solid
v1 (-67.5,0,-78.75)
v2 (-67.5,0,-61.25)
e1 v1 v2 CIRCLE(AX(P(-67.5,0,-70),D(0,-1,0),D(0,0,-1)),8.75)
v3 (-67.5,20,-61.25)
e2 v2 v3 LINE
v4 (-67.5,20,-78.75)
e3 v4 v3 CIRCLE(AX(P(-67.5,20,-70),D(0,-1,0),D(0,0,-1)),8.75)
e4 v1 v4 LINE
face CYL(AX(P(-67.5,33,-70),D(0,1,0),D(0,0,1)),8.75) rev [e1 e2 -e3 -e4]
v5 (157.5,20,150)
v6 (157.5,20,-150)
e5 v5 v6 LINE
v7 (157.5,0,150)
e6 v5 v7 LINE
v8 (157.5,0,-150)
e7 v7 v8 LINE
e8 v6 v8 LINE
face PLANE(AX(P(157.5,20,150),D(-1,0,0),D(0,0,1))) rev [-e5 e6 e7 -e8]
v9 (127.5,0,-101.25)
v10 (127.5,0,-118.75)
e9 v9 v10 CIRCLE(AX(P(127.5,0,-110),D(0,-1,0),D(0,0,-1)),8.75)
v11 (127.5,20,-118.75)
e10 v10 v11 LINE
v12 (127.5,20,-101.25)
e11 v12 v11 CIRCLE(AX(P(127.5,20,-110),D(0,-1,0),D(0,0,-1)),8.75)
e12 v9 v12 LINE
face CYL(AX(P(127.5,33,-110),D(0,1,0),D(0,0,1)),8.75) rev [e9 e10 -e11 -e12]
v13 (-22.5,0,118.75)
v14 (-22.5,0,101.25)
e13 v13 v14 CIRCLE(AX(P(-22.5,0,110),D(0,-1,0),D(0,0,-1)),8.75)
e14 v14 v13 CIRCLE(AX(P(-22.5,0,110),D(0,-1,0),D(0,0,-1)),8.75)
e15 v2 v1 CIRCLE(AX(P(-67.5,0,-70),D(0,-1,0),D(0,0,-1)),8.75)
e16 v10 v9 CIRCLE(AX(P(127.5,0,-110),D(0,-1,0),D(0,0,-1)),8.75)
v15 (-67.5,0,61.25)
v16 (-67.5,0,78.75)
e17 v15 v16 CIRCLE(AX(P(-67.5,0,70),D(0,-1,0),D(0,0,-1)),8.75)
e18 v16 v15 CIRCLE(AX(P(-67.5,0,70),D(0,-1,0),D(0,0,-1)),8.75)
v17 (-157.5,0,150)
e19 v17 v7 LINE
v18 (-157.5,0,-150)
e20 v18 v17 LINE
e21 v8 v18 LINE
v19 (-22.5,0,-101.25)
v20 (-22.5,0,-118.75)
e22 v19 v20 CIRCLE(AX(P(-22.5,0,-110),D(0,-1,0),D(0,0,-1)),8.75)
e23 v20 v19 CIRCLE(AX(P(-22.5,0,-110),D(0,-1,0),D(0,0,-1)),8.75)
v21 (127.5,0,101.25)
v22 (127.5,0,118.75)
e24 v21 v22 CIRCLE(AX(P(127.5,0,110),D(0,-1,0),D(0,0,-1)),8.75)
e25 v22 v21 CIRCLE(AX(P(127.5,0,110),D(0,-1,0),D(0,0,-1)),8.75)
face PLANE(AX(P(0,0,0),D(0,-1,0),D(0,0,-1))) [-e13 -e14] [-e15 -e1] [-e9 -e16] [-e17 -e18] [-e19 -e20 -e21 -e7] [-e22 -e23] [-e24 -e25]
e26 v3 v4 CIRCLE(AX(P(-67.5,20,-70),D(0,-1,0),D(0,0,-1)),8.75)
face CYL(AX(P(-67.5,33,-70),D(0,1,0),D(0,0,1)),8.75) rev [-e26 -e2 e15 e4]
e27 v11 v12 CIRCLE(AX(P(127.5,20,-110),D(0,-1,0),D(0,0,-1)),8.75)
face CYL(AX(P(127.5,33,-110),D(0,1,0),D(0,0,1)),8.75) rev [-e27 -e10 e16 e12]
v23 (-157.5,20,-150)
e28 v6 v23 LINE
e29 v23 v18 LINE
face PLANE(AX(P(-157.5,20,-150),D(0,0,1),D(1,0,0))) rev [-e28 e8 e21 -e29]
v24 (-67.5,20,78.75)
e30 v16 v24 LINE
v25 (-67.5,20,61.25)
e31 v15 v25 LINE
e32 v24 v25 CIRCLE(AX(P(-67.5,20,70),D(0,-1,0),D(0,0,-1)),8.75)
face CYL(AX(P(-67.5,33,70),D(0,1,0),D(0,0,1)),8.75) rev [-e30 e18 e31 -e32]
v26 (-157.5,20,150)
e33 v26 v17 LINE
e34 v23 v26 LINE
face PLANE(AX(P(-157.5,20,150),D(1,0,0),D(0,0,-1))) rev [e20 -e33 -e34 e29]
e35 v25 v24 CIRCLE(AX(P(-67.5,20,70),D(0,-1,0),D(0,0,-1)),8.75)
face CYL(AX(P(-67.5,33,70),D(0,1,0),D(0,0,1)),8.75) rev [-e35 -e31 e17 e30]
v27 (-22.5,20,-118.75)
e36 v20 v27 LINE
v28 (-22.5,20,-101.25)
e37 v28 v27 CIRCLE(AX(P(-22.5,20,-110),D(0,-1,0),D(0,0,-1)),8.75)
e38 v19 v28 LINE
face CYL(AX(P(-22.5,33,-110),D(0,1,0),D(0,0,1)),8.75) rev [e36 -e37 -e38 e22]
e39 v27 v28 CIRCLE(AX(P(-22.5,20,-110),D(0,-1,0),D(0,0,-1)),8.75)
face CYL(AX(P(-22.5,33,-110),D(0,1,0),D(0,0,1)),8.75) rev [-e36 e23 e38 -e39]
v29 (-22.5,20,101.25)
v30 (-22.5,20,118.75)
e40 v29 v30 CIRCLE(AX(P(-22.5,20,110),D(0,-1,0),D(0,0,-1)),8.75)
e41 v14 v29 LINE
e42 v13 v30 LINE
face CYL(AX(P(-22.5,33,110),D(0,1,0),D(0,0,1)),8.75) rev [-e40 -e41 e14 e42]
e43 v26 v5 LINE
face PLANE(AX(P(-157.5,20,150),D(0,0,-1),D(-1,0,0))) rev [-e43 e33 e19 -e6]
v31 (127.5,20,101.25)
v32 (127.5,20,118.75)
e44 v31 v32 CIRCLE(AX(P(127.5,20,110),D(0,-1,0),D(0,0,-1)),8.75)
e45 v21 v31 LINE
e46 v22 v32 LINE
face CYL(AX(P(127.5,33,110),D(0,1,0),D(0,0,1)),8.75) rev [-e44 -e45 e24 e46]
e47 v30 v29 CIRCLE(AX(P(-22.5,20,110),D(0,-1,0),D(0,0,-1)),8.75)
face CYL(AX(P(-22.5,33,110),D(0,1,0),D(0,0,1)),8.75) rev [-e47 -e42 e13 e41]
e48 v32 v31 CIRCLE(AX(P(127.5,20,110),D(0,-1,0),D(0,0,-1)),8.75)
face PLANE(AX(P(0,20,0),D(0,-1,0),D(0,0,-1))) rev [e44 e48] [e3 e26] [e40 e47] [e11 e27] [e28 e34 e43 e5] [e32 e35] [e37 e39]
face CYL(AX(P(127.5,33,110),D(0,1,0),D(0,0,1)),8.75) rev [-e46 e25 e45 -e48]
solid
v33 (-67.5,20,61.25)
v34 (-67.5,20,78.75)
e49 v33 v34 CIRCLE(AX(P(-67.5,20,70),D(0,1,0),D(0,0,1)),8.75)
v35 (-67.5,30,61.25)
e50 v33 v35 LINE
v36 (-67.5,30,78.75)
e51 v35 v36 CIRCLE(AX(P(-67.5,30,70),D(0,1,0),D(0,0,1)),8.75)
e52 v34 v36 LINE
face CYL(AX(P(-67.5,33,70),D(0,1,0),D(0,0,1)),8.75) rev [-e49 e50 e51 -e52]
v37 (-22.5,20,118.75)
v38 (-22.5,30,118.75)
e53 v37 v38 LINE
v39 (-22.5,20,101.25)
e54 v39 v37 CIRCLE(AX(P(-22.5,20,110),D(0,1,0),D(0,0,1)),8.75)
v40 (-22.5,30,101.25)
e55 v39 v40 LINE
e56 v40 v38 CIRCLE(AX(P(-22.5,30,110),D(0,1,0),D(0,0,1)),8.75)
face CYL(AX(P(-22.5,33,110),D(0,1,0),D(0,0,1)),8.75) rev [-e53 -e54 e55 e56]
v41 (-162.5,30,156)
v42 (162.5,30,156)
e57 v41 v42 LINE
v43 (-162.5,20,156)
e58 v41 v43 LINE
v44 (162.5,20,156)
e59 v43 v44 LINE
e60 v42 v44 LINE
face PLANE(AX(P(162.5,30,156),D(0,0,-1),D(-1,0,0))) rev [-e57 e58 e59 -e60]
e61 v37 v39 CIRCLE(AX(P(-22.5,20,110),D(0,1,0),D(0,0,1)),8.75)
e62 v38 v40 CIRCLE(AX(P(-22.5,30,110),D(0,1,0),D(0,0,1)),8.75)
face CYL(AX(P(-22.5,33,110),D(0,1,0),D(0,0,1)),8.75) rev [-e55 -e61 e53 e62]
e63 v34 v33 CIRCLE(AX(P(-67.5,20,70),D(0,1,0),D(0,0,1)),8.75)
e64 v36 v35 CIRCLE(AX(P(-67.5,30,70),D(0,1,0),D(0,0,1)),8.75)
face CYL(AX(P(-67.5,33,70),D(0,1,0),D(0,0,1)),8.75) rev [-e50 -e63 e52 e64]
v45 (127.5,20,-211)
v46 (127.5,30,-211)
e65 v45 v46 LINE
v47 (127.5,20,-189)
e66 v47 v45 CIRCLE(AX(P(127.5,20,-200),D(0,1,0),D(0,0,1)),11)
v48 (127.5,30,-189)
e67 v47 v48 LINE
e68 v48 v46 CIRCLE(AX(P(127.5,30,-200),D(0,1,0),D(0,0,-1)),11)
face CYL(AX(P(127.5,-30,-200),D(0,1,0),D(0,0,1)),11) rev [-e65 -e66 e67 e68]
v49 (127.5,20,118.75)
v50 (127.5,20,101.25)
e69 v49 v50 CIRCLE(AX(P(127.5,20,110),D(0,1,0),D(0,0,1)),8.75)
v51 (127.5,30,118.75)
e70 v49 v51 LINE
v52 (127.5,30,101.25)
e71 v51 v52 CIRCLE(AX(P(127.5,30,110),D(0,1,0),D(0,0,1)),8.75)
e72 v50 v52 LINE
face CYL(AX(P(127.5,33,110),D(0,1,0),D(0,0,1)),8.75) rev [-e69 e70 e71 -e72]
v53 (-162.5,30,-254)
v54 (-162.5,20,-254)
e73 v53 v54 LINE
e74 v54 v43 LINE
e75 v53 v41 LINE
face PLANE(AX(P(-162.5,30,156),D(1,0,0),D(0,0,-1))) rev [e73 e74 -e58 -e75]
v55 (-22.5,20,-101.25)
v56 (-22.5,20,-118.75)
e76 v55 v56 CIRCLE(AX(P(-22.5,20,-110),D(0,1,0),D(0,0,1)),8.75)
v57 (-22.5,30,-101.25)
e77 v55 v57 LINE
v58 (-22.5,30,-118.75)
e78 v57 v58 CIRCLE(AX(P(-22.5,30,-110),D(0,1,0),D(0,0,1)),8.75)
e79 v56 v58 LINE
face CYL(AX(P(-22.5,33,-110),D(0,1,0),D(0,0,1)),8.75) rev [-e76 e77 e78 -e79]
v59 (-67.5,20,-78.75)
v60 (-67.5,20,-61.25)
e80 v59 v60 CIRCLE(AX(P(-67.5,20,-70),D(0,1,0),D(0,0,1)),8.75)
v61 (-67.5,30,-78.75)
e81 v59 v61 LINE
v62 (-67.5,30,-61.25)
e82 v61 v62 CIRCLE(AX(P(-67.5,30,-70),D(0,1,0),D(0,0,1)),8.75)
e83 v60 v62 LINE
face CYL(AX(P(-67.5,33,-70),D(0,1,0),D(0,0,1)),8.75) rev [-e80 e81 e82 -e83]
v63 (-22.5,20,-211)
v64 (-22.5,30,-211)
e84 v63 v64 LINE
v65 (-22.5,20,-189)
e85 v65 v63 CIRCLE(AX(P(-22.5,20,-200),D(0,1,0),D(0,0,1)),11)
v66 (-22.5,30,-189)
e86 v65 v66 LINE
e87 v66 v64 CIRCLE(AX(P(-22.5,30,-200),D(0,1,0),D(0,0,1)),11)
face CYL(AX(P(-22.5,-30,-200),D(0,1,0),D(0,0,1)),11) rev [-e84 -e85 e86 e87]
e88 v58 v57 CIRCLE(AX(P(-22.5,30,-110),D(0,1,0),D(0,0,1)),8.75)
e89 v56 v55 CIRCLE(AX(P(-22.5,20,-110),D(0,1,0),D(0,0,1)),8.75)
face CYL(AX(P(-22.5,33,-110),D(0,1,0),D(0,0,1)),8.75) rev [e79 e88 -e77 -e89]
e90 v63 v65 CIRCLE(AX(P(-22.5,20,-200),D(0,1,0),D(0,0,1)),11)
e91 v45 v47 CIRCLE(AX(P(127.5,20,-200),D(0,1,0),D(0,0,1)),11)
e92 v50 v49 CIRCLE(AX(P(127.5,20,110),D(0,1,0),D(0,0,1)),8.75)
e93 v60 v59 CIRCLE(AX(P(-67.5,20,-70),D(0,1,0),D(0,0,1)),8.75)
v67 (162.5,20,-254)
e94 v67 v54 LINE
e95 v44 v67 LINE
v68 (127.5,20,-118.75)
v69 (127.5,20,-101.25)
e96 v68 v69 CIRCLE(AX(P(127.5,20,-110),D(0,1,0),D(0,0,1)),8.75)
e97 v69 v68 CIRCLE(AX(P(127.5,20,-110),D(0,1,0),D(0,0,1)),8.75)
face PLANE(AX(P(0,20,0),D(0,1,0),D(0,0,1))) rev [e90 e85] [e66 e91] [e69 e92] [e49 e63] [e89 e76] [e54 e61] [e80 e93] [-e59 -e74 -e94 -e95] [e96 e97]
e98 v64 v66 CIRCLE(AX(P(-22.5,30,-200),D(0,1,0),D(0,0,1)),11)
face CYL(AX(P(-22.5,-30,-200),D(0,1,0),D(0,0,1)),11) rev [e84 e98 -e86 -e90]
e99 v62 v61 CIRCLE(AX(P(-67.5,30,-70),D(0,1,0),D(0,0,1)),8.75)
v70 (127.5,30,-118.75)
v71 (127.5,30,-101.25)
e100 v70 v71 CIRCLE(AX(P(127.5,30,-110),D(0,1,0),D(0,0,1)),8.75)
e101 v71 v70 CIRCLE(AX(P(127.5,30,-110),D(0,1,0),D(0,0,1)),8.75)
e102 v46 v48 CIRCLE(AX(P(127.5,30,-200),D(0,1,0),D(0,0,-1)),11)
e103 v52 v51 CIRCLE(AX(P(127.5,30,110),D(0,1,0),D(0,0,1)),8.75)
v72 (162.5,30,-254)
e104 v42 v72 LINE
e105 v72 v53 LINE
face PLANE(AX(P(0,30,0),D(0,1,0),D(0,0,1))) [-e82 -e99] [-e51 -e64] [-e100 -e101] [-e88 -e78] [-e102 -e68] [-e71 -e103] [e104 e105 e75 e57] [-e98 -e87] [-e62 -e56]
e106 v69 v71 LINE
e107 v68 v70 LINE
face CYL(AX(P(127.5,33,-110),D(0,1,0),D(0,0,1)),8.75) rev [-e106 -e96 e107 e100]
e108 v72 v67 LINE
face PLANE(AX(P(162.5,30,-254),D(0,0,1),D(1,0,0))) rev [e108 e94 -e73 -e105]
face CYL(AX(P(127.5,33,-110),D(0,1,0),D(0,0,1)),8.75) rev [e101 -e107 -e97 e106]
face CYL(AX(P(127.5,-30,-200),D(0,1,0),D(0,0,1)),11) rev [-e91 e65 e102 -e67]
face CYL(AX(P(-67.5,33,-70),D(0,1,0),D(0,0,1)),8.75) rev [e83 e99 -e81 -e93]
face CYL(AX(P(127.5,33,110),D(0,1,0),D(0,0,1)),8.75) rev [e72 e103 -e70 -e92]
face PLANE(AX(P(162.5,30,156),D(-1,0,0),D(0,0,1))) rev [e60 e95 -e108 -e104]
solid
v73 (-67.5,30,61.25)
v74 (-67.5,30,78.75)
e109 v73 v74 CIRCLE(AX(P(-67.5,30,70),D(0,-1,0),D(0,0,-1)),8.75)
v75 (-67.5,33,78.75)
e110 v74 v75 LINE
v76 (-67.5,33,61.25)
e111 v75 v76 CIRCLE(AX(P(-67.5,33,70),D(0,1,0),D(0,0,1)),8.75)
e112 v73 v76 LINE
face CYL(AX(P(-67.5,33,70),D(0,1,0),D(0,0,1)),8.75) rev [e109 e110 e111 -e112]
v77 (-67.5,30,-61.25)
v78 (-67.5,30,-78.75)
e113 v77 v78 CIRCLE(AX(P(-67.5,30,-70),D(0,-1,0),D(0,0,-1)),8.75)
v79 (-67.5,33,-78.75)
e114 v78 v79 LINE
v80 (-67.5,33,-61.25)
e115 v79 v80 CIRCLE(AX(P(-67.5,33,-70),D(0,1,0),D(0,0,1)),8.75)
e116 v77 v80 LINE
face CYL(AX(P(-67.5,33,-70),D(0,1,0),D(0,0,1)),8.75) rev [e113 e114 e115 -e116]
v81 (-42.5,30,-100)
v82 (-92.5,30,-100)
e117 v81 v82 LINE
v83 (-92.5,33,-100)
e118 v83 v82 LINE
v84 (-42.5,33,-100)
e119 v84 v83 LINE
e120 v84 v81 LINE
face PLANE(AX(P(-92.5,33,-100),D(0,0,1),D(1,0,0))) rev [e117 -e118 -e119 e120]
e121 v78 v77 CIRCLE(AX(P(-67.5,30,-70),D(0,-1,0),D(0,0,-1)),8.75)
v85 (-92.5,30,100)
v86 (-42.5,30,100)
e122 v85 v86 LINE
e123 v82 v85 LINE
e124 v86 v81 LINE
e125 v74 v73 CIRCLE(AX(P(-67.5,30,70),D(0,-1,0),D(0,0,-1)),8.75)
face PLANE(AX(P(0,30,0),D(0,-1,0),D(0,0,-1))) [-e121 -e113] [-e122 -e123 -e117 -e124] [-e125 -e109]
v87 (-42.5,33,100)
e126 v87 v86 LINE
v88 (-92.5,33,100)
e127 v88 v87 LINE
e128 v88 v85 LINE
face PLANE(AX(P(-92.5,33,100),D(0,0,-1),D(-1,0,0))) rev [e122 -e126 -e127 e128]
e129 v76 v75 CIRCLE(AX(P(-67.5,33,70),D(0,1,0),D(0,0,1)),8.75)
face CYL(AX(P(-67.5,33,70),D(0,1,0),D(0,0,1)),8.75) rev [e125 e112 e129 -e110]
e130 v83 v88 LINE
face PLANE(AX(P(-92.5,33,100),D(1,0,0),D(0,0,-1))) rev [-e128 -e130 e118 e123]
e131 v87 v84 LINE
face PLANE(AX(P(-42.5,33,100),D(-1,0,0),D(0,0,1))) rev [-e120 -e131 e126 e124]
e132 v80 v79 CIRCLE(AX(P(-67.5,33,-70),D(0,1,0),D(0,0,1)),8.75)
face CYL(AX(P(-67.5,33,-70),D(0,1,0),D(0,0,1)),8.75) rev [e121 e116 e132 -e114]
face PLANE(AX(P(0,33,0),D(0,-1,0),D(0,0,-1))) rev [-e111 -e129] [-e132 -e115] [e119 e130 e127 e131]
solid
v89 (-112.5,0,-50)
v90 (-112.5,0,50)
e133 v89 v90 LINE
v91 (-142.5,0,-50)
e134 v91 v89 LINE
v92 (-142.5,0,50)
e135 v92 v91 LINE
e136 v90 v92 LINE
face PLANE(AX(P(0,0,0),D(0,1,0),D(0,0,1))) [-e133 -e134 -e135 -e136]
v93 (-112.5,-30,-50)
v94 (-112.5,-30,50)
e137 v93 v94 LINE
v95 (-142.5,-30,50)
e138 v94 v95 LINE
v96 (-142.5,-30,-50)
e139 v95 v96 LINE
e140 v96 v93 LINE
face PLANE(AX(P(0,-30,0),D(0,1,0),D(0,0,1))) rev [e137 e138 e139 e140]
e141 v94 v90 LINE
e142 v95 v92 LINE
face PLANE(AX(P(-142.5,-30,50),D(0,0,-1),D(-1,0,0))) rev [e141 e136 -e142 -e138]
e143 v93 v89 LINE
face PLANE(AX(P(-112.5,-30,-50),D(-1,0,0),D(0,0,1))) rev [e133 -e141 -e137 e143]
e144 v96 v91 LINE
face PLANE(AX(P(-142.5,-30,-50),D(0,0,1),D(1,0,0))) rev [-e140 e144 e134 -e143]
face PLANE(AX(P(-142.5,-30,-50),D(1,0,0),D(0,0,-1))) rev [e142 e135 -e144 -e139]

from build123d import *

# Parameters (mm, degrees)
SKETCH_1_W                   = 315
SKETCH_1_H                   = 300
EXTRUDE_1_DEPTH              = 20
SKETCH_2_W                   = 325
SKETCH_2_H                   = 410
EXTRUDE_2_DEPTH              = 10
SKETCH_3_W                   = 50
SKETCH_3_H                   = 200
EXTRUDE_3_DEPTH              = 3
SKETCH_4_W                   = 30
SKETCH_4_H                   = 100
EXTRUDE_4_DEPTH              = 30
HOLE_WIZARD_M20_1_AT_2_COUNT = 2
HOLE_WIZARD_M20_1_AT_2_PITCH = 60.207972894
HOLE_WIZARD_M20_1_AT_3_COUNT = 2
HOLE_WIZARD_M20_1_AT_3_PITCH = 185.539753153
HOLE_WIZARD_M20_1_AT_4_COUNT = 2
HOLE_WIZARD_M20_1_AT_4_PITCH = 140
HOLE_WIZARD_M20_1_AT_5_COUNT = 2
HOLE_WIZARD_M20_1_AT_5_PITCH = 265.377090194
HOLE_WIZARD_M20_1_AT_6_COUNT = 2
HOLE_WIZARD_M20_1_AT_6_PITCH = 199.060292374
SKETCH_5_R                   = 11
CUT_EXTRUDE_1_DEPTH          = 308.444710477


with BuildPart() as part:
    # 草图1 → 凸台-拉伸1 (new body)
    with BuildSketch(Plane(origin=(0, 0, 0), x_dir=(1, 0, 0), z_dir=(0, 1, 0))):
        Rectangle(SKETCH_1_W, SKETCH_1_H)
    extrude(amount=EXTRUDE_1_DEPTH)


with BuildPart() as body_2:
    # 草图2 → 凸台-拉伸2 (new body)
    with BuildSketch(Plane(origin=(0, 20, 0), x_dir=(1, 0, 0), z_dir=(0, 1, 0))):
        with Locations((0, 49)):
            Rectangle(SKETCH_2_W, SKETCH_2_H)
    extrude(amount=EXTRUDE_2_DEPTH)


with BuildPart() as body_3:
    # 草图3 → 凸台-拉伸3 (new body)
    with BuildSketch(Plane(origin=(0, 30, 0), x_dir=(1, 0, 0), z_dir=(0, 1, 0))):
        with Locations((-67.5, 0)):
            Rectangle(SKETCH_3_W, SKETCH_3_H)
    extrude(amount=EXTRUDE_3_DEPTH)


with BuildPart() as body_4:
    # 草图4 → 凸台-拉伸4 (new body)
    with BuildSketch(Plane.XZ):
        with Locations((-127.5, 0)):
            Rectangle(SKETCH_4_W, SKETCH_4_H)
    extrude(amount=EXTRUDE_4_DEPTH)


with BuildPart() as hole_wizard_m20_1_tool:
    # 草图7 → M20 螺纹孔1 (revolve)
    with BuildSketch(Plane(origin=(-67.5, 33, -70), x_dir=(0, 0, 1), z_dir=(1, 0, 0))):
        Polygon((0, 0), (0, 57.757530416), (8.75, 52.5), (8.75, 0), align=None)
    hole_wizard_m20_1 = revolve(axis=Axis((-67.5, 39.35, -70), (0, -1, 0)))


with BuildPart() as part_1:
    add(part.part)

    # M20 螺纹孔1: cut by hole_wizard_m20_1_tool
    add(hole_wizard_m20_1_tool.part, mode=Mode.SUBTRACT)


with BuildPart() as body_2_1:
    add(body_2.part)

    # M20 螺纹孔1: cut by hole_wizard_m20_1_tool
    add(hole_wizard_m20_1_tool.part, mode=Mode.SUBTRACT)


with BuildPart() as body_3_1:
    add(body_3.part)

    # M20 螺纹孔1: cut by hole_wizard_m20_1_tool
    add(hole_wizard_m20_1_tool.part, mode=Mode.SUBTRACT)


with BuildPart() as hole_wizard_m20_1_at_2_tool:
    # M20 螺纹孔1 at 2: M20 螺纹孔1 ×2
    with Locations(*[Vector(0.7474093186836596, 0, -0.6643638388299199) * (i * HOLE_WIZARD_M20_1_AT_2_PITCH) for i in range(1, HOLE_WIZARD_M20_1_AT_2_COUNT)]):
        add(hole_wizard_m20_1)


with BuildPart() as part_2:
    add(part_1.part)

    # M20 螺纹孔1 at 2: cut by hole_wizard_m20_1_at_2_tool
    add(hole_wizard_m20_1_at_2_tool.part, mode=Mode.SUBTRACT)


with BuildPart() as body_2_2:
    add(body_2_1.part)

    # M20 螺纹孔1 at 2: cut by hole_wizard_m20_1_at_2_tool
    add(hole_wizard_m20_1_at_2_tool.part, mode=Mode.SUBTRACT)


with BuildPart() as hole_wizard_m20_1_at_3_tool:
    # M20 螺纹孔1 at 3: M20 螺纹孔1 ×2
    with Locations(*[Vector(0.2425356250363329, 0, 0.970142500145332) * (i * HOLE_WIZARD_M20_1_AT_3_PITCH) for i in range(1, HOLE_WIZARD_M20_1_AT_3_COUNT)]):
        add(hole_wizard_m20_1)


with BuildPart() as part_3:
    add(part_2.part)

    # M20 螺纹孔1 at 3: cut by hole_wizard_m20_1_at_3_tool
    add(hole_wizard_m20_1_at_3_tool.part, mode=Mode.SUBTRACT)


with BuildPart() as body_2_3:
    add(body_2_2.part)

    # M20 螺纹孔1 at 3: cut by hole_wizard_m20_1_at_3_tool
    add(hole_wizard_m20_1_at_3_tool.part, mode=Mode.SUBTRACT)


with BuildPart() as hole_wizard_m20_1_at_4_tool:
    # M20 螺纹孔1 at 4: M20 螺纹孔1 ×2
    with Locations(*[(0, 0, i * HOLE_WIZARD_M20_1_AT_4_PITCH) for i in range(1, HOLE_WIZARD_M20_1_AT_4_COUNT)]):
        add(hole_wizard_m20_1)


with BuildPart() as part_4:
    add(part_3.part)

    # M20 螺纹孔1 at 4: cut by hole_wizard_m20_1_at_4_tool
    add(hole_wizard_m20_1_at_4_tool.part, mode=Mode.SUBTRACT)


with BuildPart() as body_2_4:
    add(body_2_3.part)

    # M20 螺纹孔1 at 4: cut by hole_wizard_m20_1_at_4_tool
    add(hole_wizard_m20_1_at_4_tool.part, mode=Mode.SUBTRACT)


with BuildPart() as body_3_2:
    add(body_3_1.part)

    # M20 螺纹孔1 at 4: cut by hole_wizard_m20_1_at_4_tool
    add(hole_wizard_m20_1_at_4_tool.part, mode=Mode.SUBTRACT)


with BuildPart() as hole_wizard_m20_1_at_5_tool:
    # M20 螺纹孔1 at 5: M20 螺纹孔1 ×2
    with Locations(*[Vector(0.7348034446274881, 0, 0.6782801027330657) * (i * HOLE_WIZARD_M20_1_AT_5_PITCH) for i in range(1, HOLE_WIZARD_M20_1_AT_5_COUNT)]):
        add(hole_wizard_m20_1)


with BuildPart() as part_5:
    add(part_4.part)

    # M20 螺纹孔1 at 5: cut by hole_wizard_m20_1_at_5_tool
    add(hole_wizard_m20_1_at_5_tool.part, mode=Mode.SUBTRACT)


with BuildPart() as body_2_5:
    add(body_2_4.part)

    # M20 螺纹孔1 at 5: cut by hole_wizard_m20_1_at_5_tool
    add(hole_wizard_m20_1_at_5_tool.part, mode=Mode.SUBTRACT)


with BuildPart() as hole_wizard_m20_1_at_6_tool:
    # M20 螺纹孔1 at 6: M20 螺纹孔1 ×2
    with Locations(*[Vector(0.9796027006414901, 0, -0.20094414372133138) * (i * HOLE_WIZARD_M20_1_AT_6_PITCH) for i in range(1, HOLE_WIZARD_M20_1_AT_6_COUNT)]):
        add(hole_wizard_m20_1)


with BuildPart() as part_6:
    add(part_5.part)

    # M20 螺纹孔1 at 6: cut by hole_wizard_m20_1_at_6_tool
    add(hole_wizard_m20_1_at_6_tool.part, mode=Mode.SUBTRACT)


with BuildPart() as body_2_6:
    add(body_2_5.part)

    # M20 螺纹孔1 at 6: cut by hole_wizard_m20_1_at_6_tool
    add(hole_wizard_m20_1_at_6_tool.part, mode=Mode.SUBTRACT)

    # 草图5 → 切除-拉伸1 (cut, through all)
    with BuildSketch(Plane(origin=(0, 30, 0), x_dir=(1, 0, 0), z_dir=(0, 1, 0))):
        with Locations(Location((-22.5, 200, 0), (0, 0, 270))):
            Circle(SKETCH_5_R)
        with Locations(Location((127.5, 200, 0), (0, 0, 270))):
            Circle(SKETCH_5_R)
    extrude(amount=-CUT_EXTRUDE_1_DEPTH, mode=Mode.SUBTRACT)


solid = Compound([body_4.part, body_3_2.part, part_6.part, body_2_6.part])
